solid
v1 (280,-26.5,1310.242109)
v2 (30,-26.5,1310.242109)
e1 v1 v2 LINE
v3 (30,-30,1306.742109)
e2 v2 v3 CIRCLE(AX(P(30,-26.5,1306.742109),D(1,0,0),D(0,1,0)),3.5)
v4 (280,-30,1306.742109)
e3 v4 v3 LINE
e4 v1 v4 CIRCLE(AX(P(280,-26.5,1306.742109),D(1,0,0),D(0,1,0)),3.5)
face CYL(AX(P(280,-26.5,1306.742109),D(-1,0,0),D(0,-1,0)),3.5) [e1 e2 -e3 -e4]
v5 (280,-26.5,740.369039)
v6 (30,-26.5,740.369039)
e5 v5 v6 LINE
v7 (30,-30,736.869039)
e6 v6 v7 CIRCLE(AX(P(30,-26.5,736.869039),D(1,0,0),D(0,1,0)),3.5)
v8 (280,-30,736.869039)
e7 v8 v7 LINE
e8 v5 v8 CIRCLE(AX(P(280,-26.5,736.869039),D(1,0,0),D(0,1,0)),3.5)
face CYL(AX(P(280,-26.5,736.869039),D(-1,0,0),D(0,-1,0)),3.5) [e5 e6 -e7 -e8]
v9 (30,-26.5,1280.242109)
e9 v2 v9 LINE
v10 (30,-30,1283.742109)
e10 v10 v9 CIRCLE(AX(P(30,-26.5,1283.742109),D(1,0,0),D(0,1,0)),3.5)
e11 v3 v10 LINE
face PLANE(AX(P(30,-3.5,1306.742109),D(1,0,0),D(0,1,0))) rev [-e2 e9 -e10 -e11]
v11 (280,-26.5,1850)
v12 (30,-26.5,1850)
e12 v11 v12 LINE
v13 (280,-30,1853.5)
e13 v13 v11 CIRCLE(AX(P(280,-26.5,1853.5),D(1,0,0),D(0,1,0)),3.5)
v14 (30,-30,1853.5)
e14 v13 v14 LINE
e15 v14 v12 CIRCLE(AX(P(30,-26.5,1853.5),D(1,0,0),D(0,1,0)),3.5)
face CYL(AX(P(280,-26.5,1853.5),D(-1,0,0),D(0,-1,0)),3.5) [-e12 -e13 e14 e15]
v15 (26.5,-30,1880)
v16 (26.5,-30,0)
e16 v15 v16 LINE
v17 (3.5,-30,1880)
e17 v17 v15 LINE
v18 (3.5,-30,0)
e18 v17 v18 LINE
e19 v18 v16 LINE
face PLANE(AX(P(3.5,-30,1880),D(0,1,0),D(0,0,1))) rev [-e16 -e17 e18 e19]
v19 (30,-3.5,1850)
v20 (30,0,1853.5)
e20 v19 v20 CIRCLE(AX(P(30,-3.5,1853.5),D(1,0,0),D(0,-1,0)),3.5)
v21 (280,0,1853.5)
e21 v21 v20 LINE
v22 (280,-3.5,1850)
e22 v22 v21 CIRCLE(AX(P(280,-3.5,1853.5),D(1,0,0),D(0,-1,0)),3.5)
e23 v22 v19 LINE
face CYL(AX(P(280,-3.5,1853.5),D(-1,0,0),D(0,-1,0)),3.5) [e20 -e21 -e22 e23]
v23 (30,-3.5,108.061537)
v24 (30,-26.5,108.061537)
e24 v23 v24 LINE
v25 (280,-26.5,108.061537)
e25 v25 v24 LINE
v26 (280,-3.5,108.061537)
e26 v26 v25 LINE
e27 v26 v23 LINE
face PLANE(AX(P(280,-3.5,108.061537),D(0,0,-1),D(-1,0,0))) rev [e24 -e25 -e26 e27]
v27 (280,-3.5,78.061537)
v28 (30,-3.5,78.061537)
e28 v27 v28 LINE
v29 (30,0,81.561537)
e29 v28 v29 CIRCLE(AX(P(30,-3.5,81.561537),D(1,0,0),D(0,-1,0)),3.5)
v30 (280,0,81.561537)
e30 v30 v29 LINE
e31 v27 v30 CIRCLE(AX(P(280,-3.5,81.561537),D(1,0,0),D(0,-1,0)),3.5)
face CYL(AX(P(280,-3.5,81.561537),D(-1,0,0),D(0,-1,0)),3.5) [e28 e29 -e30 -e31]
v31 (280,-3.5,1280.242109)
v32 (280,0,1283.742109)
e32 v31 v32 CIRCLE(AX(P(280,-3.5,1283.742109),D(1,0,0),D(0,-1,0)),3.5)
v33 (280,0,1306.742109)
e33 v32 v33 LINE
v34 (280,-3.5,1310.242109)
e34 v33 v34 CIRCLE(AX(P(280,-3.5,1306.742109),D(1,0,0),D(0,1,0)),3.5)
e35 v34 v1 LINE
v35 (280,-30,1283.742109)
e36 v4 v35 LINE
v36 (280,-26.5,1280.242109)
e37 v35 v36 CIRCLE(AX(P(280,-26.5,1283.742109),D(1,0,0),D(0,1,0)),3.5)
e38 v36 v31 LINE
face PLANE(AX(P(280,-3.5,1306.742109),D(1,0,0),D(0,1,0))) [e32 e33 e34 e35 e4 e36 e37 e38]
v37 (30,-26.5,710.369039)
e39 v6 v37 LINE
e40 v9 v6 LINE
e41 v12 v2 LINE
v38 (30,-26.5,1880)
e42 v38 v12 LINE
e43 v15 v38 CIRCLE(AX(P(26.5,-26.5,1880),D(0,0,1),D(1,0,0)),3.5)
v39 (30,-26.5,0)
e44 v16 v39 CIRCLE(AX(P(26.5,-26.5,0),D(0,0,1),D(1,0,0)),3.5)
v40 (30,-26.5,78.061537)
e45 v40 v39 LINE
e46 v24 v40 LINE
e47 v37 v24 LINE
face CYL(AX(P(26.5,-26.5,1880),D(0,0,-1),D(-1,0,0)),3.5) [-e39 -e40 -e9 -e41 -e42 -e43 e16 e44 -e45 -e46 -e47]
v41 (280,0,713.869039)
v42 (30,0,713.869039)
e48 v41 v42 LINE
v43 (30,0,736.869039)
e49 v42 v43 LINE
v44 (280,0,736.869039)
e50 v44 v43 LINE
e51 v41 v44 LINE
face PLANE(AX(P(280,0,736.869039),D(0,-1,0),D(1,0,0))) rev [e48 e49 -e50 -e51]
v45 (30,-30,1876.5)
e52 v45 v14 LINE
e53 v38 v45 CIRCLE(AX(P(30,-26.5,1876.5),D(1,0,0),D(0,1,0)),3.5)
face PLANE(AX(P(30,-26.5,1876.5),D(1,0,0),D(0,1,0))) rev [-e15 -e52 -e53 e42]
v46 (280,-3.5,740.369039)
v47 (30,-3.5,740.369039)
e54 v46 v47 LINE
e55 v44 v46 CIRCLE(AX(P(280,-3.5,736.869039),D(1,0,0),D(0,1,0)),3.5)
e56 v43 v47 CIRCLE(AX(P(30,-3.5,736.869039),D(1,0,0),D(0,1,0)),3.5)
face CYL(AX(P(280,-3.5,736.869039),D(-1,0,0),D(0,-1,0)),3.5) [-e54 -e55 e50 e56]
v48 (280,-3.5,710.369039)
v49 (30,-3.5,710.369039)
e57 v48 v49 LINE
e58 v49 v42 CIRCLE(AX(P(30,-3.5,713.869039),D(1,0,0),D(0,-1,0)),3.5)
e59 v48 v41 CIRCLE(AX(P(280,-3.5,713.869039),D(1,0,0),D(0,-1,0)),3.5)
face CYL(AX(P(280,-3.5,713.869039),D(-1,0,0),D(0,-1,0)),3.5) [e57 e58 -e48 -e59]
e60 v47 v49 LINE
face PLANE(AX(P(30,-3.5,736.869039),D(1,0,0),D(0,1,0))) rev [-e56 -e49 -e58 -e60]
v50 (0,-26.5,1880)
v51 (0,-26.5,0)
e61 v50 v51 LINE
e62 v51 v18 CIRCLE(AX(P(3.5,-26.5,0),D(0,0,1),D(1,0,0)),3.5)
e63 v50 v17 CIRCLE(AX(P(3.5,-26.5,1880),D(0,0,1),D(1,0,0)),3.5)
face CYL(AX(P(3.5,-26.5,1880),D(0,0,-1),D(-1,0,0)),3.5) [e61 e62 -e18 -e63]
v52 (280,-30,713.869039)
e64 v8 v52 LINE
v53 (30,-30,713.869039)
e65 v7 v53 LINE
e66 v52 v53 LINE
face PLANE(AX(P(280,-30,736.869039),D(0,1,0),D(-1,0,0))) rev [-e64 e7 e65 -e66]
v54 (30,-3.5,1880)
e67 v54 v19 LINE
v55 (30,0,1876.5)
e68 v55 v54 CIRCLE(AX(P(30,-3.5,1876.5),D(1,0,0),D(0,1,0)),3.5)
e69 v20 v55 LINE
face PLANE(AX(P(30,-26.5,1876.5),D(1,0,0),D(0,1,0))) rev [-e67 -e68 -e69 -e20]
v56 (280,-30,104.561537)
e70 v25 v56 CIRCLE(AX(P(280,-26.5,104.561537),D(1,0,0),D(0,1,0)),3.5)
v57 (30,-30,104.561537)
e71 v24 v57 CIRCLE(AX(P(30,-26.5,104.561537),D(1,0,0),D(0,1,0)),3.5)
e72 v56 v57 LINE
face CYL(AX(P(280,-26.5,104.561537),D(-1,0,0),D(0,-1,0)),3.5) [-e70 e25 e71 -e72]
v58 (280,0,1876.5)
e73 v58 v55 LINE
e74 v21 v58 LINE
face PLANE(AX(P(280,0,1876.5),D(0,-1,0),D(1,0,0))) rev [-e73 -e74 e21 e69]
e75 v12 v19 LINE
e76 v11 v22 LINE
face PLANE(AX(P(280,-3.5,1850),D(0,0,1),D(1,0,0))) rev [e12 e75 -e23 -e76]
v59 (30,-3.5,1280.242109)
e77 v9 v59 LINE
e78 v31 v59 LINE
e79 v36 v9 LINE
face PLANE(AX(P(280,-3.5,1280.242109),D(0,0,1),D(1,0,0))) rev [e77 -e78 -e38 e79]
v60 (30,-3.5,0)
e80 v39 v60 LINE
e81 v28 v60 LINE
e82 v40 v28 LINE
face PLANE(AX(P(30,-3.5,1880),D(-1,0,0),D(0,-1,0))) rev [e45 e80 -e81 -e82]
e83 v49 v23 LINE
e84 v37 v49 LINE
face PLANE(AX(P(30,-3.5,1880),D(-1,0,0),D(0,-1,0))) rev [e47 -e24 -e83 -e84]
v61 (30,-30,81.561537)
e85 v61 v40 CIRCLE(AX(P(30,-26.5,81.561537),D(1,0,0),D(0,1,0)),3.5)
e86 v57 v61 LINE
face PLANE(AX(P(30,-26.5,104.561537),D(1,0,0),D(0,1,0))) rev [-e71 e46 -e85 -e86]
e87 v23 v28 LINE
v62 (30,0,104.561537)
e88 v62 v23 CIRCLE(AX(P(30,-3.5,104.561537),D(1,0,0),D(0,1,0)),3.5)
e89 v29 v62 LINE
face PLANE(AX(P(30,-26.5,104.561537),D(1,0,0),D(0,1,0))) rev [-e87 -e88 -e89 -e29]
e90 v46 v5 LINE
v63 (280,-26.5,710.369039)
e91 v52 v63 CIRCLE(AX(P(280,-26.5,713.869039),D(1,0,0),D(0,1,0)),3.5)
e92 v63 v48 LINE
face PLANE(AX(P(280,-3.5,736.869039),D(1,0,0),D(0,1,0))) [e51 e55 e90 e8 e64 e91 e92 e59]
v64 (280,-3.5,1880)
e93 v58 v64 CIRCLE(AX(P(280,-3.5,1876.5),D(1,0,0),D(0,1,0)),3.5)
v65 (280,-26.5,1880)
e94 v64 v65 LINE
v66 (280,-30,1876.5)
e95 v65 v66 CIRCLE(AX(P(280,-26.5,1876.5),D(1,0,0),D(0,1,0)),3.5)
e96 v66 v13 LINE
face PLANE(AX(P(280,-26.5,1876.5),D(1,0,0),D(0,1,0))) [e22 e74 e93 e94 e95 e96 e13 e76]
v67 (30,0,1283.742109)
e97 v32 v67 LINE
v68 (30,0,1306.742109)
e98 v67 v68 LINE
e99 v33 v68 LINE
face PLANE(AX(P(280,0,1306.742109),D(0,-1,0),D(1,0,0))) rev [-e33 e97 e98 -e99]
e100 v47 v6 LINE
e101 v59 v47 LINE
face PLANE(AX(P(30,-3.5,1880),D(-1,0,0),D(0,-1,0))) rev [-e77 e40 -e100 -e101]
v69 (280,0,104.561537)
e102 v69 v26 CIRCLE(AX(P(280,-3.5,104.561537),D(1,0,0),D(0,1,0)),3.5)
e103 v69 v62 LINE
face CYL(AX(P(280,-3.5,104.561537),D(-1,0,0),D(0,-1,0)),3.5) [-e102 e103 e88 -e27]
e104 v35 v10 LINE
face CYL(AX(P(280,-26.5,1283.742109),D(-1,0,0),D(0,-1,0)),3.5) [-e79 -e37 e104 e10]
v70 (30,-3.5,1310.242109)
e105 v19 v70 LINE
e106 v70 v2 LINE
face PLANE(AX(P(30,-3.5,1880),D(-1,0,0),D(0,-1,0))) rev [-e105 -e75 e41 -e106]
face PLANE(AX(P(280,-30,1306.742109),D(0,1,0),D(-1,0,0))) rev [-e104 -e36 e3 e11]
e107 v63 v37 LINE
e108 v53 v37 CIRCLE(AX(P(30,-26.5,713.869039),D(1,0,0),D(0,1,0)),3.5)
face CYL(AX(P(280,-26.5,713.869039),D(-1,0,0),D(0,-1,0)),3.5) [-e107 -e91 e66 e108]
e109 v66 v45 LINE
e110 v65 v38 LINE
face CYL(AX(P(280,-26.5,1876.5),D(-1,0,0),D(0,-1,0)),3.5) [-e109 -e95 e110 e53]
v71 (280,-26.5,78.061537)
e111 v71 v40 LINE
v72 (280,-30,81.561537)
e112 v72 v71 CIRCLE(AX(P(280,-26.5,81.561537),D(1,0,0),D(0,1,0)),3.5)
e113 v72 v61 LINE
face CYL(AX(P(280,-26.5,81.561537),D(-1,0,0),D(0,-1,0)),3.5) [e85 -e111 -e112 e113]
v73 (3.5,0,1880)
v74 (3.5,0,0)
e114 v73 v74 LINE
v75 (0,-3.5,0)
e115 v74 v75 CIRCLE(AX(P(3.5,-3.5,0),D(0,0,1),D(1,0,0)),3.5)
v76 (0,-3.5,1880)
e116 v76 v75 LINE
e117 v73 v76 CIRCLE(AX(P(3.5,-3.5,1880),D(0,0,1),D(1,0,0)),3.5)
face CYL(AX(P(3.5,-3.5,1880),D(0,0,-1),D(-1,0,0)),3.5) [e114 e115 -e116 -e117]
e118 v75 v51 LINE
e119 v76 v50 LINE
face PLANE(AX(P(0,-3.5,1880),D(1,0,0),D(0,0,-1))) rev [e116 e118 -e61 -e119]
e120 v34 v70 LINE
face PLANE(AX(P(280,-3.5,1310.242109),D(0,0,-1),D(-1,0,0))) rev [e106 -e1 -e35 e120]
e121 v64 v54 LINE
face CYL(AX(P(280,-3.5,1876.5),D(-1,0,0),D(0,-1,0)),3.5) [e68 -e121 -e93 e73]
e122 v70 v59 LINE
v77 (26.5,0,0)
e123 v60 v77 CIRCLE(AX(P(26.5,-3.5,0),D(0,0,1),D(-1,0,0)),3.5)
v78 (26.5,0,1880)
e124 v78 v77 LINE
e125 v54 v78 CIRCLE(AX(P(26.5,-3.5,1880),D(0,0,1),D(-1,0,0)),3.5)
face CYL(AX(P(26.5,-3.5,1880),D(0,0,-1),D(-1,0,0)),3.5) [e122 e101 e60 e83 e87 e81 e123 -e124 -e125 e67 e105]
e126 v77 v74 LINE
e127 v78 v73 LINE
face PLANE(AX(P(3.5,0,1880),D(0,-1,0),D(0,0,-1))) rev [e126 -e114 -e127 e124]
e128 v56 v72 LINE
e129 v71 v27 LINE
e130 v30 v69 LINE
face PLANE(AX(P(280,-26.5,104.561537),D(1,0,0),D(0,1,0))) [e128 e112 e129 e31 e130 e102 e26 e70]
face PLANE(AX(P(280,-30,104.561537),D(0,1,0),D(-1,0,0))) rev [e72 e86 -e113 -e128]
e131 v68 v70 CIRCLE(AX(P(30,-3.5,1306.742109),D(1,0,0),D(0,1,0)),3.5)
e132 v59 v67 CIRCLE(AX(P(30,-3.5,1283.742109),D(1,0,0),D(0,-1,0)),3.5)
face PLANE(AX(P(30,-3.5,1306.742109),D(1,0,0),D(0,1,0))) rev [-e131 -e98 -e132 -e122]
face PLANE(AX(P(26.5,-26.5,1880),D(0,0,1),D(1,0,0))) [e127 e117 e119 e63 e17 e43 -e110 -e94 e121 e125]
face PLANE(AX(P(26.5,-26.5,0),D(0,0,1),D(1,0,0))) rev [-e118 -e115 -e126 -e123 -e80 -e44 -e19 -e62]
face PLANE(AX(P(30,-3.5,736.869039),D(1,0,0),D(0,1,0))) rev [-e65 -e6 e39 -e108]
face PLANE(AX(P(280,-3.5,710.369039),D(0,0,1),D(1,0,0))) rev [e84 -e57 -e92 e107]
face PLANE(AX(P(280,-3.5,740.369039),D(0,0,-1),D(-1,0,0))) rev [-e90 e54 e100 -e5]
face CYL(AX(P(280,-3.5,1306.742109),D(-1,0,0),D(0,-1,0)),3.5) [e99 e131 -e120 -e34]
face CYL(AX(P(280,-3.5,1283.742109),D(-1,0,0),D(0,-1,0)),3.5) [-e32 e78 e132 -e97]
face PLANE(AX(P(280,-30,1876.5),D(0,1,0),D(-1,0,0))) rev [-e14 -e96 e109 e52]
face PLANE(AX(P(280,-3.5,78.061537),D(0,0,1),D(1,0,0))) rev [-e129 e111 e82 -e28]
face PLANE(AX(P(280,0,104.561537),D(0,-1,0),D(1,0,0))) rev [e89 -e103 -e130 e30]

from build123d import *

# Parameters (mm, degrees)
BOSS_EXTRUDE1_DEPTH = 1880
BOSS_EXTRUDE2_DEPTH = 250


with BuildPart() as part:
    # Sketch1 → Boss-Extrude1 (new body)
    with BuildSketch(Plane.XY):
        with BuildLine():
            Line((3.5, 0), (26.5, 0))
            ThreePointArc((26.5, 0), (28.974873734, -1.025126266), (30, -3.5))
            Line((30, -3.5), (30, -26.5))
            ThreePointArc((30, -26.5), (28.974873734, -28.974873734), (26.5, -30))
            Line((26.5, -30), (3.5, -30))
            ThreePointArc((3.5, -30), (1.025126266, -28.974873734), (0, -26.5))
            Line((0, -26.5), (0, -3.5))
            ThreePointArc((0, -3.5), (1.025126266, -1.025126266), (3.5, 0))
        make_face()
    extrude(amount=BOSS_EXTRUDE1_DEPTH)

    # Sketch2 → Boss-Extrude2 (add)
    with BuildSketch(Plane(origin=(30, 0, 0), x_dir=(0, 0, -1), z_dir=(1, 0, 0))):
        with BuildLine():
            Line((-1876.5, 0), (-1853.5, 0))
            ThreePointArc((-1853.5, 0), (-1851.025126266, -1.025126266), (-1850, -3.5))
            Line((-1850, -3.5), (-1850, -26.5))
            ThreePointArc((-1850, -26.5), (-1851.025126266, -28.974873734), (-1853.5, -30))
            Line((-1853.5, -30), (-1876.5, -30))
            ThreePointArc((-1876.5, -30), (-1878.974873734, -28.974873734), (-1880, -26.5))
            Line((-1880, -26.5), (-1880, -3.5))
            ThreePointArc((-1880, -3.5), (-1878.974873734, -1.025126266), (-1876.5, 0))
        make_face()
        with BuildLine():
            Line((-104.561536833, 0), (-81.561536833, 0))
            ThreePointArc((-81.561536833, 0), (-79.086663099, -1.025126266), (-78.061536833, -3.5))
            Line((-78.061536833, -3.5), (-78.061536833, -26.5))
            ThreePointArc((-78.061536833, -26.5), (-79.086663099, -28.974873734), (-81.561536833, -30))
            Line((-81.561536833, -30), (-104.561536833, -30))
            ThreePointArc((-104.561536833, -30), (-107.036410567, -28.974873734), (-108.061536833, -26.5))
            Line((-108.061536833, -26.5), (-108.061536833, -3.5))
            ThreePointArc((-108.061536833, -3.5), (-107.036410567, -1.025126266), (-104.561536833, 0))
        make_face()
        with BuildLine():
            Line((-1306.742108749, 0), (-1283.742108749, 0))
            ThreePointArc((-1283.742108749, 0), (-1281.267235014, -1.025126266), (-1280.242108749, -3.5))
            Line((-1280.242108749, -3.5), (-1280.242108749, -26.5))
            ThreePointArc((-1280.242108749, -26.5), (-1281.267235014, -28.974873734), (-1283.742108749, -30))
            Line((-1283.742108749, -30), (-1306.742108749, -30))
            ThreePointArc((-1306.742108749, -30), (-1309.216982483, -28.974873734), (-1310.242108749, -26.5))
            Line((-1310.242108749, -26.5), (-1310.242108749, -3.5))
            ThreePointArc((-1310.242108749, -3.5), (-1309.216982483, -1.025126266), (-1306.742108749, 0))
        make_face()
        with BuildLine():
            Line((-736.86903894, 0), (-713.86903894, 0))
            ThreePointArc((-713.86903894, 0), (-711.394165206, -1.025126266), (-710.36903894, -3.5))
            Line((-710.36903894, -3.5), (-710.36903894, -26.5))
            ThreePointArc((-710.36903894, -26.5), (-711.394165206, -28.974873734), (-713.86903894, -30))
            Line((-713.86903894, -30), (-736.86903894, -30))
            ThreePointArc((-736.86903894, -30), (-739.343912674, -28.974873734), (-740.36903894, -26.5))
            Line((-740.36903894, -26.5), (-740.36903894, -3.5))
            ThreePointArc((-740.36903894, -3.5), (-739.343912674, -1.025126266), (-736.86903894, 0))
        make_face()
    extrude(amount=BOSS_EXTRUDE2_DEPTH)


solid = part.part
